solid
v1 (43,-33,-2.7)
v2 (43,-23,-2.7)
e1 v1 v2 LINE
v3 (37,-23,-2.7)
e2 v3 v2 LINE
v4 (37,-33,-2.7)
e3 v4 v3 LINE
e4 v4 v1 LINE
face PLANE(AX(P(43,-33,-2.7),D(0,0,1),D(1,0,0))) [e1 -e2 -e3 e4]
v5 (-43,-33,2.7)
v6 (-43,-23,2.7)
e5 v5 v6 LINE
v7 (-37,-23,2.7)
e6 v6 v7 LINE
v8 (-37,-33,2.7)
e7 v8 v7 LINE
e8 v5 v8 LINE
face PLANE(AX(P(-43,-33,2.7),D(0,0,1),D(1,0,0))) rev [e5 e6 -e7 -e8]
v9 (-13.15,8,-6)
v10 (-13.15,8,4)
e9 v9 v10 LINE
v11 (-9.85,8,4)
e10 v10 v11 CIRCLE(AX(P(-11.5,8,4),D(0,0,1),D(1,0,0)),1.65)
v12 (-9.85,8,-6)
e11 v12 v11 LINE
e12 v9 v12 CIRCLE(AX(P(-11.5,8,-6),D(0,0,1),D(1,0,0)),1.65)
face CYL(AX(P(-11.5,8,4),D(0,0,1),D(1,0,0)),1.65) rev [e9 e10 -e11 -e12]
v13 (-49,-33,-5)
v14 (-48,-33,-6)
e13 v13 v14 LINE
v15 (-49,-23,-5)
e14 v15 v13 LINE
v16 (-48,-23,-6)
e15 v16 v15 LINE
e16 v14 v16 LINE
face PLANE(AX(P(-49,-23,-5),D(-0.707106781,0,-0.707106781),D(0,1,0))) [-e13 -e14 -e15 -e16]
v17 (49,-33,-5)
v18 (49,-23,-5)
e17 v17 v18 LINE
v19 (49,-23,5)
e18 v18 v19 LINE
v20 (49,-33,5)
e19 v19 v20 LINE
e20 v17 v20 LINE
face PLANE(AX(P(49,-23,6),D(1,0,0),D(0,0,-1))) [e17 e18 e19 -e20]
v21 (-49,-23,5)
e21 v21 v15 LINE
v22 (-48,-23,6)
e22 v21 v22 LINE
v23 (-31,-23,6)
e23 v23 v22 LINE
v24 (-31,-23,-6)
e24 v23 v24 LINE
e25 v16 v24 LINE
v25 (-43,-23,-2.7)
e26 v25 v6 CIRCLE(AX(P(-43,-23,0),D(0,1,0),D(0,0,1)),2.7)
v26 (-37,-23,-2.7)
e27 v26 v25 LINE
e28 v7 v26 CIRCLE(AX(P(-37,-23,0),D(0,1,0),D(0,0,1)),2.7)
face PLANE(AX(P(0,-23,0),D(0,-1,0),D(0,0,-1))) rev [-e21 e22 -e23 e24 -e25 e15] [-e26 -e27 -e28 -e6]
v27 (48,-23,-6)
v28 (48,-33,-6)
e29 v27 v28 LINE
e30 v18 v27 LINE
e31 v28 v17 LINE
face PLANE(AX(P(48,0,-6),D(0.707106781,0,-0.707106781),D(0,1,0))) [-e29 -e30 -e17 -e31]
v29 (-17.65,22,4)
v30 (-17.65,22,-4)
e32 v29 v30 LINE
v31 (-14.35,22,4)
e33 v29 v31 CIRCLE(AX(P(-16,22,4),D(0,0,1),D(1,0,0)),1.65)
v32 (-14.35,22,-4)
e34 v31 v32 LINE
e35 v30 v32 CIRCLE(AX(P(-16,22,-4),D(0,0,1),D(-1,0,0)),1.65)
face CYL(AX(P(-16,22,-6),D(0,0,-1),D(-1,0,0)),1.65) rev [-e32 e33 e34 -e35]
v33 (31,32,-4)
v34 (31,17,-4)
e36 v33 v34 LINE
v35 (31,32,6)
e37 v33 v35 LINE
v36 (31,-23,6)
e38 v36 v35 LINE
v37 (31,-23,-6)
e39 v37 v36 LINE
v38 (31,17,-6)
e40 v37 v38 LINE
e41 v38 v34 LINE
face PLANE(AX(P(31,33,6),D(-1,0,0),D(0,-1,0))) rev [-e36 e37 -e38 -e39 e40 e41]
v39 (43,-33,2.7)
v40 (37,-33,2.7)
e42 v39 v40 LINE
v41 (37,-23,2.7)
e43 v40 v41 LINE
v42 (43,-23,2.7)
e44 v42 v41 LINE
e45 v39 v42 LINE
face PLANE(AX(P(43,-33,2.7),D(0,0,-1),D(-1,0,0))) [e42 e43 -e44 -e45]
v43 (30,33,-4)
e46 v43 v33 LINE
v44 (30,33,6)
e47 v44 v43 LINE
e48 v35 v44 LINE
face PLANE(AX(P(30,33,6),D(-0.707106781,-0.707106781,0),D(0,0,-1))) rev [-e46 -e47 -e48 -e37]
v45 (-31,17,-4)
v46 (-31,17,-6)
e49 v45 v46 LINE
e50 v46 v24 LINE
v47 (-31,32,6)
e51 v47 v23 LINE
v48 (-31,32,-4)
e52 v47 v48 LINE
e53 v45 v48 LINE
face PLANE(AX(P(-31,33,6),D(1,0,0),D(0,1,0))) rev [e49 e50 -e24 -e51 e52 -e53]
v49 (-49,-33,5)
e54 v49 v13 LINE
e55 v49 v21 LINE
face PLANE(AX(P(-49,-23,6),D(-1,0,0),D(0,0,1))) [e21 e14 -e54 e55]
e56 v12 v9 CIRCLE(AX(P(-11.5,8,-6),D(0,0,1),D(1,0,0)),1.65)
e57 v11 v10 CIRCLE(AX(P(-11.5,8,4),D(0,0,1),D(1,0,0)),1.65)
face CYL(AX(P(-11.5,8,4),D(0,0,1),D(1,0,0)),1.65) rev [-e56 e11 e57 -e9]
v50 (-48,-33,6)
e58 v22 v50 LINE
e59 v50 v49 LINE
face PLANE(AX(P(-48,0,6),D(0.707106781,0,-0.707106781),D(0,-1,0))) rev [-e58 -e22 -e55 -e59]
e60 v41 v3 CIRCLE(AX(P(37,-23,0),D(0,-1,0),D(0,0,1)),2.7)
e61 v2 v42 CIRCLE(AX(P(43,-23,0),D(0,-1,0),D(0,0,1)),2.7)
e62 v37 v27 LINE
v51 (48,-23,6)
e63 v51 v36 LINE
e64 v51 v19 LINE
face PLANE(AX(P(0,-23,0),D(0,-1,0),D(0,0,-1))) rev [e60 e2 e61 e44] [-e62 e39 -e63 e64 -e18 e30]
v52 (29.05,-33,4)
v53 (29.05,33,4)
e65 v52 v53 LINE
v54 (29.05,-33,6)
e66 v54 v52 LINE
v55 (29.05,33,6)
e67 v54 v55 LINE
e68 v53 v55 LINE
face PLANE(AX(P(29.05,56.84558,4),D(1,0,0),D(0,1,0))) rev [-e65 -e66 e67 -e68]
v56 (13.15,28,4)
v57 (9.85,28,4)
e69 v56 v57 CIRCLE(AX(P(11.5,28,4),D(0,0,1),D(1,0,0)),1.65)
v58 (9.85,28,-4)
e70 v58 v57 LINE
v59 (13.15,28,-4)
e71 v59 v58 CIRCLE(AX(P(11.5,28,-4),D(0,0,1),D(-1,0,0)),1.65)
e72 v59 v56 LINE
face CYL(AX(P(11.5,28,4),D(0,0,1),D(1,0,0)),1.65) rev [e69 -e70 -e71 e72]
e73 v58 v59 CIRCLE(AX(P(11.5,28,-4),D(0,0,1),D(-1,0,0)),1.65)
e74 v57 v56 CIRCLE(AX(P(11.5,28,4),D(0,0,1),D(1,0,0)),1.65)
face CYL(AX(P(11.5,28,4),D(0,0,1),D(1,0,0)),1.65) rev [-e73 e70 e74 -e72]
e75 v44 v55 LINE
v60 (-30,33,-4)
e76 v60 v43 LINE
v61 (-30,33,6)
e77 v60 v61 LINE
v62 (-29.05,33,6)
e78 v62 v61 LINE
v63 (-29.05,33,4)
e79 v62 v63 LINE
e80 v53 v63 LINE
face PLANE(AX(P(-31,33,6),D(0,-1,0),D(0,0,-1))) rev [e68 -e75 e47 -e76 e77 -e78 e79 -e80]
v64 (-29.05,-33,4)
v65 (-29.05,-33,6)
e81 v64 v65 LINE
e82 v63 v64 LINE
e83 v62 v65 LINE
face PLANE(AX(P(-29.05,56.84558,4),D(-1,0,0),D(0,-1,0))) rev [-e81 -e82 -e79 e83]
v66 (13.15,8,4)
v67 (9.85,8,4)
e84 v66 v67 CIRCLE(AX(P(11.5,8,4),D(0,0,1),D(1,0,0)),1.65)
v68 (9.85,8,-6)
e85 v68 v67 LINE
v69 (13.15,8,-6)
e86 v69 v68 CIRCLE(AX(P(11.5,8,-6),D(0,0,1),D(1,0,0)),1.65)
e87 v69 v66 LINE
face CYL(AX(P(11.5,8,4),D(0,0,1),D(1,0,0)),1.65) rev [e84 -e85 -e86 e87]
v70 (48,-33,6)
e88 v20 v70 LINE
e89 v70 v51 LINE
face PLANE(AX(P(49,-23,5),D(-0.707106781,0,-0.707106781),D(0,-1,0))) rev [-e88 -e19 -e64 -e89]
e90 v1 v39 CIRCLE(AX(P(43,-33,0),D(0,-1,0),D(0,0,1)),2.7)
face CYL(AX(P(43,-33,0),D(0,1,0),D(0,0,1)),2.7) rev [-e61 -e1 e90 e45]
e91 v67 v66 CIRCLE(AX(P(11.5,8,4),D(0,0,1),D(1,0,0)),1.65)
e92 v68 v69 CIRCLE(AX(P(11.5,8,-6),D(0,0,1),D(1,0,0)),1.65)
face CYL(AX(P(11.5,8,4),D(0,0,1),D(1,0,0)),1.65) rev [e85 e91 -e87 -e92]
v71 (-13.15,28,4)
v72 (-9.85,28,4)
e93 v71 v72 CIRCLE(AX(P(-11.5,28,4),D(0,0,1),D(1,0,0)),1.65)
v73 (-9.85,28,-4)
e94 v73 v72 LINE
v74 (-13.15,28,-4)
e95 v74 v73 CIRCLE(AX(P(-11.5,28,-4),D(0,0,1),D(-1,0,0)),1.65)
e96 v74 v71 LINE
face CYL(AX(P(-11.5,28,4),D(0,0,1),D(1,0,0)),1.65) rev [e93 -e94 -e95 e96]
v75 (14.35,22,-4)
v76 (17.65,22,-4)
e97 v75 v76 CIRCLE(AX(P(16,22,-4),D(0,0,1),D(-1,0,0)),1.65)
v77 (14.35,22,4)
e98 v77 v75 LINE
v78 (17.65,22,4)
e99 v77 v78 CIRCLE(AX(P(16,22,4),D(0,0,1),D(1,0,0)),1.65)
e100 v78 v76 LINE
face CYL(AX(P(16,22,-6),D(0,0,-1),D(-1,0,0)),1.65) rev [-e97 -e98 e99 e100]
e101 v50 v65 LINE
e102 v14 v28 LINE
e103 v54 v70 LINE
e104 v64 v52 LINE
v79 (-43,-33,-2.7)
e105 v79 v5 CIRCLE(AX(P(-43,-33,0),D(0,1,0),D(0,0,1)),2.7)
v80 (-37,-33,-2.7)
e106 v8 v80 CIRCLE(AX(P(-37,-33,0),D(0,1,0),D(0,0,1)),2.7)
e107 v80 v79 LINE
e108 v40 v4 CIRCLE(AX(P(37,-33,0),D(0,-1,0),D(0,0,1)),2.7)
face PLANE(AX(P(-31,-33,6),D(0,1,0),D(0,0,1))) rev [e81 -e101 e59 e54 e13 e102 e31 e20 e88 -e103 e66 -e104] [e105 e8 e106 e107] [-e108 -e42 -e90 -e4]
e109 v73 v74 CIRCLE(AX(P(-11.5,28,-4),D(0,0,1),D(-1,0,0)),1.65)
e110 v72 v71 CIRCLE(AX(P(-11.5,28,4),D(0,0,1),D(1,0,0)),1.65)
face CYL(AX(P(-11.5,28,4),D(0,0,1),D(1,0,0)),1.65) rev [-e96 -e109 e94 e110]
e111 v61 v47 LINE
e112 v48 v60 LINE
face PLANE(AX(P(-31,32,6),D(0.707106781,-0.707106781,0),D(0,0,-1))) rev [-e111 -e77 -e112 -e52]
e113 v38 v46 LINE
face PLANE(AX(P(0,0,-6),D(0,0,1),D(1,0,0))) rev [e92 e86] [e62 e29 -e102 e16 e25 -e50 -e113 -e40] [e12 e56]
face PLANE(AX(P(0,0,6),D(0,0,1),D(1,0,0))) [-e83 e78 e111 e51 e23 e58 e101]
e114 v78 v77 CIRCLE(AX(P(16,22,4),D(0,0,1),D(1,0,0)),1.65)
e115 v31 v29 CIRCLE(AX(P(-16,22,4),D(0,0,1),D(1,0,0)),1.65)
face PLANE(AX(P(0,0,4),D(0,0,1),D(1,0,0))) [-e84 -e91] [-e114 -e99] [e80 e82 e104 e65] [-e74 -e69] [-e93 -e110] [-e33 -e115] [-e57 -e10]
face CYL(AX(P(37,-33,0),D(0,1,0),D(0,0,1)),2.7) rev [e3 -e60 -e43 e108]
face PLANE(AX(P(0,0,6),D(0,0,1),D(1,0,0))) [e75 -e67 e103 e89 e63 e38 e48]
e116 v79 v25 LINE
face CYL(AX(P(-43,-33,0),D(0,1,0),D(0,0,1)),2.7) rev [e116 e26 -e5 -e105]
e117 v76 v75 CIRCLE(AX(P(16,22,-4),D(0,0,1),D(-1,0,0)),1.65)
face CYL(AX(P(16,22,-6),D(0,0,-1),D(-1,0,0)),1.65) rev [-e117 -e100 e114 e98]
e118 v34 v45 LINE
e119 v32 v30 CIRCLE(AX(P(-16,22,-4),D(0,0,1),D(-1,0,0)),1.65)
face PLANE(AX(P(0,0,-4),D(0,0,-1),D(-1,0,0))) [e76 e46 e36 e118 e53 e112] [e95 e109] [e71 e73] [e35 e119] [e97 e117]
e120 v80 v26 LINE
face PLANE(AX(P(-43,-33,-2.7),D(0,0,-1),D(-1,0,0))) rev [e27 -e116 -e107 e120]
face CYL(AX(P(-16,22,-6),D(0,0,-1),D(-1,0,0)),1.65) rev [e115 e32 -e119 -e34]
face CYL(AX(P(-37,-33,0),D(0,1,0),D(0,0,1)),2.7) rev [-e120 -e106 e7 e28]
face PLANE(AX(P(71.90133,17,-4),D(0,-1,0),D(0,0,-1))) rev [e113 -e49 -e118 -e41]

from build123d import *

# Parameters (mm, degrees)
SKETCH_1_W          = 62
SKETCH_1_H          = 66
EXTRUDE_1_DEPTH     = 6
SKETCH_3_W          = 58.1
SKETCH_3_H          = 113.69115984
CUT_EXTRUDE_1_DEPTH = 2
HOLE_WIZARD_M4_1_D  = 3.3
HOLE_WIZARD_M4_2_D  = 3.3
SKETCH_14_W         = 98
SKETCH_14_H         = 12
EXTRUDE_3_DEPTH     = 10
CUT_EXTRUDE_2_DEPTH = 75.652528423
SKETCH_16_W         = 58.1
SKETCH_16_H         = 41.285826149
CUT_EXTRUDE_3_DEPTH = 2
SKETCH_17_W         = 126.235416792
SKETCH_17_H         = 53.479043567
CUT_EXTRUDE_4_DEPTH = 2
CHAMFER_1_SIZE      = 1
CHAMFER_2_SIZE      = 1


with BuildPart() as part:
    # 草图1 → 凸台-拉伸1 (new, symmetric)
    with BuildSketch(Plane.XY):
        Rectangle(SKETCH_1_W, SKETCH_1_H)
    extrude(amount=EXTRUDE_1_DEPTH, both=True)

    # 草图3 → 切除-拉伸1 (cut)
    with BuildSketch(Plane.XY.offset(6)):
        Rectangle(SKETCH_3_W, SKETCH_3_H)
    extrude(amount=-CUT_EXTRUDE_1_DEPTH, mode=Mode.SUBTRACT)

    # M4 螺纹孔1 (through all)
    with Locations(Plane.XY.offset(4)):
        with Locations((-11.5, 28), (11.5, 28), (-11.5, 8), (11.5, 8)):
            Hole(HOLE_WIZARD_M4_1_D / 2)

    # M4 螺纹孔2 (through all)
    with Locations(Plane(origin=(0, 0, -6), x_dir=(-1, 0, 0), z_dir=(0, 0, -1))):
        with Locations((-16, 22), (16, 22)):
            Hole(HOLE_WIZARD_M4_2_D / 2)

    # 草图14 → 凸台-拉伸3 (add)
    with BuildSketch(Plane.XZ.offset(33)):
        Rectangle(SKETCH_14_W, SKETCH_14_H)
    extrude(amount=-EXTRUDE_3_DEPTH)

    # 草图15 → 切除-拉伸2 (cut, through all)
    with BuildSketch(Plane(origin=(0, -23, 0), x_dir=(1, 0, 0), z_dir=(0, 1, 0))):
        with BuildLine():
            Line((-43, 2.7), (-37, 2.7))
            ThreePointArc((-37, 2.7), (-34.3, 0), (-37, -2.7))
            Line((-37, -2.7), (-43, -2.7))
            ThreePointArc((-43, -2.7), (-45.7, 0), (-43, 2.7))
        make_face()
    cut_extrude_2 = extrude(amount=-CUT_EXTRUDE_2_DEPTH, mode=Mode.SUBTRACT)

    # 镜向1: 切除-拉伸2 across plane
    add(cut_extrude_2.mirror(Plane(origin=(0, 0, 0), x_dir=(0, 0, 1), z_dir=(1, 0, 0))), mode=Mode.SUBTRACT)

    # 草图16 → 切除-拉伸3 (cut)
    with BuildSketch(Plane.XY.offset(6)):
        with Locations((0, -39.137864824)):
            Rectangle(SKETCH_16_W, SKETCH_16_H)
    extrude(amount=-CUT_EXTRUDE_3_DEPTH, mode=Mode.SUBTRACT)

    # 草图17 → 切除-拉伸4 (cut)
    with BuildSketch(Plane(origin=(0, 0, -6), x_dir=(-1, 0, 0), z_dir=(0, 0, -1))):
        with Locations((-8.783621981, 43.739521784)):
            Rectangle(SKETCH_17_W, SKETCH_17_H)
    extrude(amount=-CUT_EXTRUDE_4_DEPTH, mode=Mode.SUBTRACT)

    # 倒角1
    chamfer_1_edges = [part.edges().sort_by_distance(p)[0] for p in [
        (49, -28, -6),
        (-49, -28, 6),
        (49, -28, 6),
        (-49, -28, -6),
    ]]
    chamfer(chamfer_1_edges, length=CHAMFER_1_SIZE)

    # 倒角2
    chamfer_2_edges = [part.edges().sort_by_distance(p)[0] for p in [
        (-31, 33, 1),
        (31, 33, 1),
    ]]
    chamfer(chamfer_2_edges, length=CHAMFER_2_SIZE)


solid = part.part
